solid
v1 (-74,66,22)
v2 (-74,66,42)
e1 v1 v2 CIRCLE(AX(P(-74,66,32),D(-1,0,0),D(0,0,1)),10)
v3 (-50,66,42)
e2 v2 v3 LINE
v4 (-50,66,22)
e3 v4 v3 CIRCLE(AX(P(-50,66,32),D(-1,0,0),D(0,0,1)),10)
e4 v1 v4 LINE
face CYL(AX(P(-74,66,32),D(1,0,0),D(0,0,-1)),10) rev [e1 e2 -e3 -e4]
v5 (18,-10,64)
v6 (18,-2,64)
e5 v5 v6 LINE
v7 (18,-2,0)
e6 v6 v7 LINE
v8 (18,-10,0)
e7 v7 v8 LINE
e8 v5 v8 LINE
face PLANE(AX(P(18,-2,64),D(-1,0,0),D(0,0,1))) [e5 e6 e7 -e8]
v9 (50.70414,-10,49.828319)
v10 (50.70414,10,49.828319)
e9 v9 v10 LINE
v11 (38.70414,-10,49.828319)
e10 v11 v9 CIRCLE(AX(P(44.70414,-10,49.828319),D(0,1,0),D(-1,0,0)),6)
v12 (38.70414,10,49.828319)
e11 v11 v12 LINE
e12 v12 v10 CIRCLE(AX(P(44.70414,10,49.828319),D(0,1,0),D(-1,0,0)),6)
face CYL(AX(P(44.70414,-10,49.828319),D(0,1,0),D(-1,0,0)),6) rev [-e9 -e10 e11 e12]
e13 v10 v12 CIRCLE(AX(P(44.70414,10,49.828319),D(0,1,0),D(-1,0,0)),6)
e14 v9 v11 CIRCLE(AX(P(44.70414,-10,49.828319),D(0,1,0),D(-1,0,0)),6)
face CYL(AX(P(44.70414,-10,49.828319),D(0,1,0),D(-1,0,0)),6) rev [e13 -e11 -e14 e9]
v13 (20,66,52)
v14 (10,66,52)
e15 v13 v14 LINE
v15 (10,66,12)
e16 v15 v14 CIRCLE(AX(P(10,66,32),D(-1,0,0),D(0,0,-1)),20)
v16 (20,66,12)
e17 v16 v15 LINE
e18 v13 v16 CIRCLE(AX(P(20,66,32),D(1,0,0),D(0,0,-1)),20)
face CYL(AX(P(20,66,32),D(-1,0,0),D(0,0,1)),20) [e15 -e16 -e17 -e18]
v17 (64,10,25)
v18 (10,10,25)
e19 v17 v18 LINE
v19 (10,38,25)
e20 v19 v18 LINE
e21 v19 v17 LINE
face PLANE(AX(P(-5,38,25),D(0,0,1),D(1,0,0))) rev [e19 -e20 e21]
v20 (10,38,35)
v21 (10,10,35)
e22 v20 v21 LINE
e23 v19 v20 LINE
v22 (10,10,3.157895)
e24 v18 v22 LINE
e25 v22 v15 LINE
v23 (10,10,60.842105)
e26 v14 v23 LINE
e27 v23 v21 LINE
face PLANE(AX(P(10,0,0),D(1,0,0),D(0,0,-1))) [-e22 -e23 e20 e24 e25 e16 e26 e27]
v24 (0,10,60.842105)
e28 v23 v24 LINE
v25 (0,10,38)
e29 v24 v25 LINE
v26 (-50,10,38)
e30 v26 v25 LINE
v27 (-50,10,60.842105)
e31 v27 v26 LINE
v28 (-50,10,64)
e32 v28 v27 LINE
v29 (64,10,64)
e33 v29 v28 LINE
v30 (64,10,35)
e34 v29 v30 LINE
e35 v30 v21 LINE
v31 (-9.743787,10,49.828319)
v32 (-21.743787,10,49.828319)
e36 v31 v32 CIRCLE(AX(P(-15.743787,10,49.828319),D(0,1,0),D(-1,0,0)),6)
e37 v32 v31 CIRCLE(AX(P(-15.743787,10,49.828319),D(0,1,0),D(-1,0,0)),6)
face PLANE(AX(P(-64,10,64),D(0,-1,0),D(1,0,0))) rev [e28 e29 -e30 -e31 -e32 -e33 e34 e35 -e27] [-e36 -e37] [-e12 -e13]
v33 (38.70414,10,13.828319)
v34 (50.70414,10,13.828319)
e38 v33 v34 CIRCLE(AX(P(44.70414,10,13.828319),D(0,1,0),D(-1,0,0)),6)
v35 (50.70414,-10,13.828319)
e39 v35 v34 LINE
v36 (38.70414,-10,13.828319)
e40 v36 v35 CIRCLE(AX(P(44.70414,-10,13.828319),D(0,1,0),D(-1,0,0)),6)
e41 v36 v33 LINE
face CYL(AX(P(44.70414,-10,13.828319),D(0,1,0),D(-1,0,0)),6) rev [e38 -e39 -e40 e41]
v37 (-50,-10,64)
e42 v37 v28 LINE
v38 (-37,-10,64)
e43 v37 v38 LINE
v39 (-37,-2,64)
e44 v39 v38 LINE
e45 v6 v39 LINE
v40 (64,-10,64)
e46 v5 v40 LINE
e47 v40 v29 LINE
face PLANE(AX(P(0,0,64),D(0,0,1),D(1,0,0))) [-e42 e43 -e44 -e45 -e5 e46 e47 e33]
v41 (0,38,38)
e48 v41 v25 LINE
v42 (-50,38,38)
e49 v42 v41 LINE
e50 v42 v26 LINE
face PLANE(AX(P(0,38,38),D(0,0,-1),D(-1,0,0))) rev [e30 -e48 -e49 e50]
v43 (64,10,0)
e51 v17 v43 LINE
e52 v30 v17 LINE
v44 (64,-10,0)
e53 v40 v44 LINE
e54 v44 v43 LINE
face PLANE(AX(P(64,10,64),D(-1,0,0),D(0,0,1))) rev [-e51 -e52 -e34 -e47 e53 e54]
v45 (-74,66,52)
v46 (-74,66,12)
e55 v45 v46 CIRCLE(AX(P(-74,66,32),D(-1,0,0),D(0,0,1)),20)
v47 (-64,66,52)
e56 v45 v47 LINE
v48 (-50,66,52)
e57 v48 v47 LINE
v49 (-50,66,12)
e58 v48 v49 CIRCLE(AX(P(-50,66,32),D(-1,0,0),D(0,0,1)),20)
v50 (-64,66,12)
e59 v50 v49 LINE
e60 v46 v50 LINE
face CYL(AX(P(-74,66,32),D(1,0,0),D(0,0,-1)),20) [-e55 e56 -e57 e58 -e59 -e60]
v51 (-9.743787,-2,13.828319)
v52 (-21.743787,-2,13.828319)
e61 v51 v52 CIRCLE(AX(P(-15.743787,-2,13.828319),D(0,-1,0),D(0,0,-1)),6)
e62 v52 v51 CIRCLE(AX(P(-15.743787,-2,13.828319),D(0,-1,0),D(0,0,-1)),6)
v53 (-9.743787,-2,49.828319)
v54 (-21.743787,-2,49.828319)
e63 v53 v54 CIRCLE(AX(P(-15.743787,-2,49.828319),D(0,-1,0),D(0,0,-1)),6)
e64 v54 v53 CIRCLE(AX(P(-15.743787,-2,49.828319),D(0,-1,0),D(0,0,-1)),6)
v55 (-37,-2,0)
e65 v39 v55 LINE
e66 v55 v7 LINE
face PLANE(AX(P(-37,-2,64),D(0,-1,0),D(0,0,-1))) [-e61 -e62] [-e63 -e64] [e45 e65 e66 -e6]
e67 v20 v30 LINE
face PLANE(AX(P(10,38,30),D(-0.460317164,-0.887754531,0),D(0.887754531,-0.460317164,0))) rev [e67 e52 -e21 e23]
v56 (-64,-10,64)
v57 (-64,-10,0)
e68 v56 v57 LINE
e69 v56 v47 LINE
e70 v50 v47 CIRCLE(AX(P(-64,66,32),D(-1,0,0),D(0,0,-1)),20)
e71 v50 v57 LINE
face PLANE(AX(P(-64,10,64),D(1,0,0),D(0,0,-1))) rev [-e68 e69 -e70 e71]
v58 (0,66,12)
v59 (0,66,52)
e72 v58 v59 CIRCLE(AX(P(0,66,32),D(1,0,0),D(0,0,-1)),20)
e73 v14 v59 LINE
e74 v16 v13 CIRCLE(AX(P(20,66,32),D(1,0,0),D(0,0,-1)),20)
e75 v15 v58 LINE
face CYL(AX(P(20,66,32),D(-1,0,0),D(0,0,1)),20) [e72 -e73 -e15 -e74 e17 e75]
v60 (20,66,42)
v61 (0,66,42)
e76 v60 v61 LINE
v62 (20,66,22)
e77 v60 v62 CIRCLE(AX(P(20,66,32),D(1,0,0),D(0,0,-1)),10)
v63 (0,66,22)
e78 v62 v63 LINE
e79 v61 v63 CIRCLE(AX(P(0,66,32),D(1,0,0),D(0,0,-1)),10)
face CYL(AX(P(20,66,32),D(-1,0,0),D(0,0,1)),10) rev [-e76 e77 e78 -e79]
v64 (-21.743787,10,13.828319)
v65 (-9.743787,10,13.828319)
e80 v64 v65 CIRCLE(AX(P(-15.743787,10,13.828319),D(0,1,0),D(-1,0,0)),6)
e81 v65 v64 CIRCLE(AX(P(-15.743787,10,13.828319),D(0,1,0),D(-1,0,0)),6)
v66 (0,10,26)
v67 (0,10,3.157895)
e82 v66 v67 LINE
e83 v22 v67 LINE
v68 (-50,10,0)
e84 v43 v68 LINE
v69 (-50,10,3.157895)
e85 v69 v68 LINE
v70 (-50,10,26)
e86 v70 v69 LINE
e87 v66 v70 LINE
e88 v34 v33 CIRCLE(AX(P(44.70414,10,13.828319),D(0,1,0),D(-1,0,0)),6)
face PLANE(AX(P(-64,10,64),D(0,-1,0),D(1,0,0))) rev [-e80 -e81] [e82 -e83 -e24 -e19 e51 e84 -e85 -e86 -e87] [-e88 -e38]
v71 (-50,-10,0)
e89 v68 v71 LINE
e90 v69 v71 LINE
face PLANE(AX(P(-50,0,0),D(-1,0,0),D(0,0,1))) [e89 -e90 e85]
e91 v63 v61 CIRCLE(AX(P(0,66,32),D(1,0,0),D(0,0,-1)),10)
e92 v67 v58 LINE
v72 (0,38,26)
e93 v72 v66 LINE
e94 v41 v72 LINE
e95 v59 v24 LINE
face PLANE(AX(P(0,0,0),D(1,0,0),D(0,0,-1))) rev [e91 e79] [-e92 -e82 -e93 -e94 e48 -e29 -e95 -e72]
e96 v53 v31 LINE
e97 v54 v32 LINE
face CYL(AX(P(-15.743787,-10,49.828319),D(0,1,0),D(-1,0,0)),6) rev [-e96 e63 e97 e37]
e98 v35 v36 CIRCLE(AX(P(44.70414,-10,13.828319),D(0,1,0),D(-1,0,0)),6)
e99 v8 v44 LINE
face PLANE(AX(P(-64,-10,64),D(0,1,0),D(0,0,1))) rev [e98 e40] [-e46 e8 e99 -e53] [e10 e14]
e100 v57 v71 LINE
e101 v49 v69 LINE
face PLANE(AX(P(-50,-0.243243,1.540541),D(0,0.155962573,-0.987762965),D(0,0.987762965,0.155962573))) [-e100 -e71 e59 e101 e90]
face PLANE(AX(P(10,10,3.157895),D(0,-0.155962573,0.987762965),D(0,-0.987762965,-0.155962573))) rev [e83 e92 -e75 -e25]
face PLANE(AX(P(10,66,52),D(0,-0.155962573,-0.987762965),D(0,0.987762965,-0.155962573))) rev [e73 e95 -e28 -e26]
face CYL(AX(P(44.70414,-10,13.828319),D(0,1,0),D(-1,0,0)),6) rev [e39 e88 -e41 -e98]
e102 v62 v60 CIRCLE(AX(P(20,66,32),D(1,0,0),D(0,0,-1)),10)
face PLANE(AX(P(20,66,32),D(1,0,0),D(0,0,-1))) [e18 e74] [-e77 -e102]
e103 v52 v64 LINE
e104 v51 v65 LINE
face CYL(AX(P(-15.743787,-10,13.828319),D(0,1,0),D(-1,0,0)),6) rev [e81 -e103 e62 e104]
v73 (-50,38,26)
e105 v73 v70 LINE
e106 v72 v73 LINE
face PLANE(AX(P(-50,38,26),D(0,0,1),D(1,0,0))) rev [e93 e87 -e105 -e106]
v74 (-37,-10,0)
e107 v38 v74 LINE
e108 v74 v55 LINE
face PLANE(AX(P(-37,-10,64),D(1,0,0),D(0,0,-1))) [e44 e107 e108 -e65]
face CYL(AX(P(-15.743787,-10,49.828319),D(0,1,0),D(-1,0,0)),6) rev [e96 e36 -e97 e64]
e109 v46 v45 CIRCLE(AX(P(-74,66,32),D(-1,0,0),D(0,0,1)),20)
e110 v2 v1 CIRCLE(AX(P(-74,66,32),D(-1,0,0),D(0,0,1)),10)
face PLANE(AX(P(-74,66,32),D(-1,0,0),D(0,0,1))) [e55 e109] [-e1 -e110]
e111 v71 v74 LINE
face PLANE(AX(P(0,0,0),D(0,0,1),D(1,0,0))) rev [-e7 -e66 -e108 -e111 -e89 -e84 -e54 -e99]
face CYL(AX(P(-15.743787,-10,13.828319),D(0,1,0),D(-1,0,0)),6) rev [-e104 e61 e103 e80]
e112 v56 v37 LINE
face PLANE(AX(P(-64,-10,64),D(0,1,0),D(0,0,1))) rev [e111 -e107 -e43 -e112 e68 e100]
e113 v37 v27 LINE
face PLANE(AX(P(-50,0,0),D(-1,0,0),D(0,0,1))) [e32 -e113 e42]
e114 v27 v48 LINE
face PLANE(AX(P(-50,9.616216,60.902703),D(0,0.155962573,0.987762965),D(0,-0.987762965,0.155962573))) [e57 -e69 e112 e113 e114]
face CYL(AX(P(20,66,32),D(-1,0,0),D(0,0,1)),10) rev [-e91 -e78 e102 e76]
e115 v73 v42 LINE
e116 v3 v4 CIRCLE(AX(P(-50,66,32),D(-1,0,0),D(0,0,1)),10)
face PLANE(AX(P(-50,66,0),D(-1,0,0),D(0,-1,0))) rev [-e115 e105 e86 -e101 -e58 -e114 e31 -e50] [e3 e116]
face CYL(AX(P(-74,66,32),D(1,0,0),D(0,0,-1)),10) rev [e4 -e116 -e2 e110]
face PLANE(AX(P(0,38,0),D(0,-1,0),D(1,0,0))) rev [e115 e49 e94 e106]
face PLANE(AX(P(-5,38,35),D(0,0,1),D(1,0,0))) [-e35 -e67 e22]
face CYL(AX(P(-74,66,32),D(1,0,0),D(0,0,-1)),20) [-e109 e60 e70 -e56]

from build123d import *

# Parameters (mm, degrees)
BASE_PROFILE_SKETCH_W           = 128
BASE_PROFILE_SKETCH_H           = 20
BASE_PLATE_DEPTH                = 64
UNDERSIDE_RELIEF_CUT_DEPTH      = 92.060419503
UNDERSIDE_RELIEF_CUT_DEPTH_BACK = 64
UNDERSIDE_RELIEF_SKETCH_W       = 55
UNDERSIDE_RELIEF_SKETCH_H       = 8
FIRST_UPRIGHT_SKETCH_W          = 14
FIRST_UPRIGHT_SKETCH_H          = 64
FIRST_UPRIGHT_DEPTH             = 56
FIRST_TRUNNION_BOSS_DEPTH       = 10
FIRST_TRUNNION_BOSS_DEPTH_BACK  = 14
FIRST_TRUNNION_BOSS_SKETCH_R    = 20
FIRST_TRUNNION_BOSS_SKETCH_R_2  = 10
FIRST_TRUNNION_BORE_DEPTH       = 14
FIRST_UPRIGHT_TAPER_CUT_DEPTH   = 14
CENTER_BLOCK_DEPTH              = 28
SECOND_TRUNNION_BOSS_SKETCH_R   = 20
SECOND_TRUNNION_BOSS_SKETCH_R_2 = 10
SECOND_TRUNNION_BOSS_DEPTH      = 20
SECOND_UPRIGHT_DEPTH            = 10
SECOND_TRUNNION_BORE_DEPTH      = 10
GUSSET_RIB_REACH                = 120.44
GUSSET_RIB_SKETCH_WALL_W        = 299.707341614
GUSSET_RIB_SKETCH_WALL_H        = 10
BASE_MOUNTING_HOLES_SKETCH_R    = 6
BASE_MOUNTING_HOLES_DEPTH       = 124.887045328


with BuildPart() as part:
    # Base Profile Sketch → Base Plate (new body)
    with BuildSketch(Plane.XY):
        Rectangle(BASE_PROFILE_SKETCH_W, BASE_PROFILE_SKETCH_H)
    extrude(amount=BASE_PLATE_DEPTH)

    # Underside Relief Sketch → Underside Relief Cut (cut, two sides: drawn at the far end of the back side and taken through both)
    with BuildSketch(Plane.XY.offset(-UNDERSIDE_RELIEF_CUT_DEPTH_BACK)):
        with Locations((-9.5, -6)):
            Rectangle(UNDERSIDE_RELIEF_SKETCH_W, UNDERSIDE_RELIEF_SKETCH_H)
    extrude(amount=UNDERSIDE_RELIEF_CUT_DEPTH + UNDERSIDE_RELIEF_CUT_DEPTH_BACK, mode=Mode.SUBTRACT)

    # First Upright Sketch → First Upright (add)
    with BuildSketch(Plane(origin=(0, 10, 0), x_dir=(1, 0, 0), z_dir=(0, 1, 0))):
        with Locations((-57, -32)):
            Rectangle(FIRST_UPRIGHT_SKETCH_W, FIRST_UPRIGHT_SKETCH_H)
    extrude(amount=FIRST_UPRIGHT_DEPTH)

    # First Trunnion Boss Sketch → First Trunnion Boss (add, two sides: drawn at the far end of the back side and taken through both)
    with BuildSketch(Plane.ZY.offset(64).offset(-FIRST_TRUNNION_BOSS_DEPTH_BACK)):
        with Locations((32, 66)):
            Circle(FIRST_TRUNNION_BOSS_SKETCH_R)
        with Locations((32, 66)):
            Circle(FIRST_TRUNNION_BOSS_SKETCH_R_2, mode=Mode.SUBTRACT)
    extrude(amount=FIRST_TRUNNION_BOSS_DEPTH + FIRST_TRUNNION_BOSS_DEPTH_BACK)

    # First Trunnion Bore Sketch → First Trunnion Bore (cut)
    with BuildSketch(Plane.ZY.offset(64)):
        with BuildLine():
            Line((42, 66), (22, 66))
            ThreePointArc((22, 66), (32, 56), (42, 66))
        make_face()
    extrude(amount=-FIRST_TRUNNION_BORE_DEPTH, mode=Mode.SUBTRACT)

    # First Upright Taper Sketch → First Upright Taper Cut (cut)
    with BuildSketch(Plane.ZY.offset(64)):
        Polygon((12, 66), (0, -10), (0, 66), align=None)
        Polygon((64, -10), (52, 66), (64, 66), align=None)
    extrude(amount=-FIRST_UPRIGHT_TAPER_CUT_DEPTH, mode=Mode.SUBTRACT)

    # Center Block Sketch → Center Block (add)
    with BuildSketch(Plane(origin=(0, 10, 0), x_dir=(1, 0, 0), z_dir=(0, 1, 0))):
        Polygon((-50, -32), (-50, -26), (0, -26), (0, -38), (-50, -38), align=None)
    extrude(amount=CENTER_BLOCK_DEPTH)



with BuildPart() as body_2:
    # Second Trunnion Boss Sketch → Second Trunnion Boss (new body)
    with BuildSketch(Plane(origin=(0, 0, 0), x_dir=(0, 0, -1), z_dir=(1, 0, 0))):
        with Locations(Location((-32, 66, 0), (0, 0, 180))):
            Circle(SECOND_TRUNNION_BOSS_SKETCH_R)
        with Locations(Location((-32, 66, 0), (0, 0, 180))):
            Circle(SECOND_TRUNNION_BOSS_SKETCH_R_2, mode=Mode.SUBTRACT)
    extrude(amount=SECOND_TRUNNION_BOSS_DEPTH)


with BuildPart() as part_1:
    add(part.part)

    add(body_2.part)  # Second Upright merges body 2
    # Second Upright Sketch → Second Upright (add)
    with BuildSketch(Plane(origin=(0, 0, 0), x_dir=(0, 0, -1), z_dir=(1, 0, 0))):
        Polygon((-52, 66), (-60.842105263, 10), (-3.157894737, 10), (-12, 66), align=None)
    extrude(amount=SECOND_UPRIGHT_DEPTH)

    # Second Trunnion Bore Sketch → Second Trunnion Bore (cut)
    with BuildSketch(Plane(origin=(0, 0, 0), x_dir=(0, 0, -1), z_dir=(1, 0, 0))):
        with BuildLine():
            Line((-22, 66), (-42, 66))
            ThreePointArc((-42, 66), (-32, 56), (-22, 66))
        make_face()
    extrude(amount=SECOND_TRUNNION_BORE_DEPTH, mode=Mode.SUBTRACT)

    # Gusset Rib Sketch wall → Gusset Rib (add, up to next)
    with BuildSketch(Plane(origin=(37, 24, 30), x_dir=(0.887754531449, -0.460317164455, 0), z_dir=(0.460317164455, 0.887754531449, 0)), mode=Mode.PRIVATE) as gusset_rib_sk1:
        Rectangle(GUSSET_RIB_SKETCH_WALL_W, GUSSET_RIB_SKETCH_WALL_H)
    gusset_rib_tool1 = extrude(gusset_rib_sk1.sketch, amount=-GUSSET_RIB_REACH, mode=Mode.PRIVATE) - part_1.part
    add(gusset_rib_tool1.solids().sort_by_distance((37, 24, 30))[0])

    # Base Mounting Holes Sketch → Base Mounting Holes (cut, through all)
    with BuildSketch(Plane(origin=(0, 10, 0), x_dir=(1, 0, 0), z_dir=(0, 1, 0))):
        with Locations(Location((-15.743786959, -13.828319493, 0), (0, 0, 180))):
            Circle(BASE_MOUNTING_HOLES_SKETCH_R)
        with Locations(Location((-15.743786959, -49.828319493, 0), (0, 0, 180))):
            Circle(BASE_MOUNTING_HOLES_SKETCH_R)
        with Locations(Location((44.704140343, -13.828319493, 0), (0, 0, 180))):
            Circle(BASE_MOUNTING_HOLES_SKETCH_R)
        with Locations(Location((44.704140343, -49.828319493, 0), (0, 0, 180))):
            Circle(BASE_MOUNTING_HOLES_SKETCH_R)
    extrude(amount=-BASE_MOUNTING_HOLES_DEPTH, mode=Mode.SUBTRACT)


solid = part_1.part
